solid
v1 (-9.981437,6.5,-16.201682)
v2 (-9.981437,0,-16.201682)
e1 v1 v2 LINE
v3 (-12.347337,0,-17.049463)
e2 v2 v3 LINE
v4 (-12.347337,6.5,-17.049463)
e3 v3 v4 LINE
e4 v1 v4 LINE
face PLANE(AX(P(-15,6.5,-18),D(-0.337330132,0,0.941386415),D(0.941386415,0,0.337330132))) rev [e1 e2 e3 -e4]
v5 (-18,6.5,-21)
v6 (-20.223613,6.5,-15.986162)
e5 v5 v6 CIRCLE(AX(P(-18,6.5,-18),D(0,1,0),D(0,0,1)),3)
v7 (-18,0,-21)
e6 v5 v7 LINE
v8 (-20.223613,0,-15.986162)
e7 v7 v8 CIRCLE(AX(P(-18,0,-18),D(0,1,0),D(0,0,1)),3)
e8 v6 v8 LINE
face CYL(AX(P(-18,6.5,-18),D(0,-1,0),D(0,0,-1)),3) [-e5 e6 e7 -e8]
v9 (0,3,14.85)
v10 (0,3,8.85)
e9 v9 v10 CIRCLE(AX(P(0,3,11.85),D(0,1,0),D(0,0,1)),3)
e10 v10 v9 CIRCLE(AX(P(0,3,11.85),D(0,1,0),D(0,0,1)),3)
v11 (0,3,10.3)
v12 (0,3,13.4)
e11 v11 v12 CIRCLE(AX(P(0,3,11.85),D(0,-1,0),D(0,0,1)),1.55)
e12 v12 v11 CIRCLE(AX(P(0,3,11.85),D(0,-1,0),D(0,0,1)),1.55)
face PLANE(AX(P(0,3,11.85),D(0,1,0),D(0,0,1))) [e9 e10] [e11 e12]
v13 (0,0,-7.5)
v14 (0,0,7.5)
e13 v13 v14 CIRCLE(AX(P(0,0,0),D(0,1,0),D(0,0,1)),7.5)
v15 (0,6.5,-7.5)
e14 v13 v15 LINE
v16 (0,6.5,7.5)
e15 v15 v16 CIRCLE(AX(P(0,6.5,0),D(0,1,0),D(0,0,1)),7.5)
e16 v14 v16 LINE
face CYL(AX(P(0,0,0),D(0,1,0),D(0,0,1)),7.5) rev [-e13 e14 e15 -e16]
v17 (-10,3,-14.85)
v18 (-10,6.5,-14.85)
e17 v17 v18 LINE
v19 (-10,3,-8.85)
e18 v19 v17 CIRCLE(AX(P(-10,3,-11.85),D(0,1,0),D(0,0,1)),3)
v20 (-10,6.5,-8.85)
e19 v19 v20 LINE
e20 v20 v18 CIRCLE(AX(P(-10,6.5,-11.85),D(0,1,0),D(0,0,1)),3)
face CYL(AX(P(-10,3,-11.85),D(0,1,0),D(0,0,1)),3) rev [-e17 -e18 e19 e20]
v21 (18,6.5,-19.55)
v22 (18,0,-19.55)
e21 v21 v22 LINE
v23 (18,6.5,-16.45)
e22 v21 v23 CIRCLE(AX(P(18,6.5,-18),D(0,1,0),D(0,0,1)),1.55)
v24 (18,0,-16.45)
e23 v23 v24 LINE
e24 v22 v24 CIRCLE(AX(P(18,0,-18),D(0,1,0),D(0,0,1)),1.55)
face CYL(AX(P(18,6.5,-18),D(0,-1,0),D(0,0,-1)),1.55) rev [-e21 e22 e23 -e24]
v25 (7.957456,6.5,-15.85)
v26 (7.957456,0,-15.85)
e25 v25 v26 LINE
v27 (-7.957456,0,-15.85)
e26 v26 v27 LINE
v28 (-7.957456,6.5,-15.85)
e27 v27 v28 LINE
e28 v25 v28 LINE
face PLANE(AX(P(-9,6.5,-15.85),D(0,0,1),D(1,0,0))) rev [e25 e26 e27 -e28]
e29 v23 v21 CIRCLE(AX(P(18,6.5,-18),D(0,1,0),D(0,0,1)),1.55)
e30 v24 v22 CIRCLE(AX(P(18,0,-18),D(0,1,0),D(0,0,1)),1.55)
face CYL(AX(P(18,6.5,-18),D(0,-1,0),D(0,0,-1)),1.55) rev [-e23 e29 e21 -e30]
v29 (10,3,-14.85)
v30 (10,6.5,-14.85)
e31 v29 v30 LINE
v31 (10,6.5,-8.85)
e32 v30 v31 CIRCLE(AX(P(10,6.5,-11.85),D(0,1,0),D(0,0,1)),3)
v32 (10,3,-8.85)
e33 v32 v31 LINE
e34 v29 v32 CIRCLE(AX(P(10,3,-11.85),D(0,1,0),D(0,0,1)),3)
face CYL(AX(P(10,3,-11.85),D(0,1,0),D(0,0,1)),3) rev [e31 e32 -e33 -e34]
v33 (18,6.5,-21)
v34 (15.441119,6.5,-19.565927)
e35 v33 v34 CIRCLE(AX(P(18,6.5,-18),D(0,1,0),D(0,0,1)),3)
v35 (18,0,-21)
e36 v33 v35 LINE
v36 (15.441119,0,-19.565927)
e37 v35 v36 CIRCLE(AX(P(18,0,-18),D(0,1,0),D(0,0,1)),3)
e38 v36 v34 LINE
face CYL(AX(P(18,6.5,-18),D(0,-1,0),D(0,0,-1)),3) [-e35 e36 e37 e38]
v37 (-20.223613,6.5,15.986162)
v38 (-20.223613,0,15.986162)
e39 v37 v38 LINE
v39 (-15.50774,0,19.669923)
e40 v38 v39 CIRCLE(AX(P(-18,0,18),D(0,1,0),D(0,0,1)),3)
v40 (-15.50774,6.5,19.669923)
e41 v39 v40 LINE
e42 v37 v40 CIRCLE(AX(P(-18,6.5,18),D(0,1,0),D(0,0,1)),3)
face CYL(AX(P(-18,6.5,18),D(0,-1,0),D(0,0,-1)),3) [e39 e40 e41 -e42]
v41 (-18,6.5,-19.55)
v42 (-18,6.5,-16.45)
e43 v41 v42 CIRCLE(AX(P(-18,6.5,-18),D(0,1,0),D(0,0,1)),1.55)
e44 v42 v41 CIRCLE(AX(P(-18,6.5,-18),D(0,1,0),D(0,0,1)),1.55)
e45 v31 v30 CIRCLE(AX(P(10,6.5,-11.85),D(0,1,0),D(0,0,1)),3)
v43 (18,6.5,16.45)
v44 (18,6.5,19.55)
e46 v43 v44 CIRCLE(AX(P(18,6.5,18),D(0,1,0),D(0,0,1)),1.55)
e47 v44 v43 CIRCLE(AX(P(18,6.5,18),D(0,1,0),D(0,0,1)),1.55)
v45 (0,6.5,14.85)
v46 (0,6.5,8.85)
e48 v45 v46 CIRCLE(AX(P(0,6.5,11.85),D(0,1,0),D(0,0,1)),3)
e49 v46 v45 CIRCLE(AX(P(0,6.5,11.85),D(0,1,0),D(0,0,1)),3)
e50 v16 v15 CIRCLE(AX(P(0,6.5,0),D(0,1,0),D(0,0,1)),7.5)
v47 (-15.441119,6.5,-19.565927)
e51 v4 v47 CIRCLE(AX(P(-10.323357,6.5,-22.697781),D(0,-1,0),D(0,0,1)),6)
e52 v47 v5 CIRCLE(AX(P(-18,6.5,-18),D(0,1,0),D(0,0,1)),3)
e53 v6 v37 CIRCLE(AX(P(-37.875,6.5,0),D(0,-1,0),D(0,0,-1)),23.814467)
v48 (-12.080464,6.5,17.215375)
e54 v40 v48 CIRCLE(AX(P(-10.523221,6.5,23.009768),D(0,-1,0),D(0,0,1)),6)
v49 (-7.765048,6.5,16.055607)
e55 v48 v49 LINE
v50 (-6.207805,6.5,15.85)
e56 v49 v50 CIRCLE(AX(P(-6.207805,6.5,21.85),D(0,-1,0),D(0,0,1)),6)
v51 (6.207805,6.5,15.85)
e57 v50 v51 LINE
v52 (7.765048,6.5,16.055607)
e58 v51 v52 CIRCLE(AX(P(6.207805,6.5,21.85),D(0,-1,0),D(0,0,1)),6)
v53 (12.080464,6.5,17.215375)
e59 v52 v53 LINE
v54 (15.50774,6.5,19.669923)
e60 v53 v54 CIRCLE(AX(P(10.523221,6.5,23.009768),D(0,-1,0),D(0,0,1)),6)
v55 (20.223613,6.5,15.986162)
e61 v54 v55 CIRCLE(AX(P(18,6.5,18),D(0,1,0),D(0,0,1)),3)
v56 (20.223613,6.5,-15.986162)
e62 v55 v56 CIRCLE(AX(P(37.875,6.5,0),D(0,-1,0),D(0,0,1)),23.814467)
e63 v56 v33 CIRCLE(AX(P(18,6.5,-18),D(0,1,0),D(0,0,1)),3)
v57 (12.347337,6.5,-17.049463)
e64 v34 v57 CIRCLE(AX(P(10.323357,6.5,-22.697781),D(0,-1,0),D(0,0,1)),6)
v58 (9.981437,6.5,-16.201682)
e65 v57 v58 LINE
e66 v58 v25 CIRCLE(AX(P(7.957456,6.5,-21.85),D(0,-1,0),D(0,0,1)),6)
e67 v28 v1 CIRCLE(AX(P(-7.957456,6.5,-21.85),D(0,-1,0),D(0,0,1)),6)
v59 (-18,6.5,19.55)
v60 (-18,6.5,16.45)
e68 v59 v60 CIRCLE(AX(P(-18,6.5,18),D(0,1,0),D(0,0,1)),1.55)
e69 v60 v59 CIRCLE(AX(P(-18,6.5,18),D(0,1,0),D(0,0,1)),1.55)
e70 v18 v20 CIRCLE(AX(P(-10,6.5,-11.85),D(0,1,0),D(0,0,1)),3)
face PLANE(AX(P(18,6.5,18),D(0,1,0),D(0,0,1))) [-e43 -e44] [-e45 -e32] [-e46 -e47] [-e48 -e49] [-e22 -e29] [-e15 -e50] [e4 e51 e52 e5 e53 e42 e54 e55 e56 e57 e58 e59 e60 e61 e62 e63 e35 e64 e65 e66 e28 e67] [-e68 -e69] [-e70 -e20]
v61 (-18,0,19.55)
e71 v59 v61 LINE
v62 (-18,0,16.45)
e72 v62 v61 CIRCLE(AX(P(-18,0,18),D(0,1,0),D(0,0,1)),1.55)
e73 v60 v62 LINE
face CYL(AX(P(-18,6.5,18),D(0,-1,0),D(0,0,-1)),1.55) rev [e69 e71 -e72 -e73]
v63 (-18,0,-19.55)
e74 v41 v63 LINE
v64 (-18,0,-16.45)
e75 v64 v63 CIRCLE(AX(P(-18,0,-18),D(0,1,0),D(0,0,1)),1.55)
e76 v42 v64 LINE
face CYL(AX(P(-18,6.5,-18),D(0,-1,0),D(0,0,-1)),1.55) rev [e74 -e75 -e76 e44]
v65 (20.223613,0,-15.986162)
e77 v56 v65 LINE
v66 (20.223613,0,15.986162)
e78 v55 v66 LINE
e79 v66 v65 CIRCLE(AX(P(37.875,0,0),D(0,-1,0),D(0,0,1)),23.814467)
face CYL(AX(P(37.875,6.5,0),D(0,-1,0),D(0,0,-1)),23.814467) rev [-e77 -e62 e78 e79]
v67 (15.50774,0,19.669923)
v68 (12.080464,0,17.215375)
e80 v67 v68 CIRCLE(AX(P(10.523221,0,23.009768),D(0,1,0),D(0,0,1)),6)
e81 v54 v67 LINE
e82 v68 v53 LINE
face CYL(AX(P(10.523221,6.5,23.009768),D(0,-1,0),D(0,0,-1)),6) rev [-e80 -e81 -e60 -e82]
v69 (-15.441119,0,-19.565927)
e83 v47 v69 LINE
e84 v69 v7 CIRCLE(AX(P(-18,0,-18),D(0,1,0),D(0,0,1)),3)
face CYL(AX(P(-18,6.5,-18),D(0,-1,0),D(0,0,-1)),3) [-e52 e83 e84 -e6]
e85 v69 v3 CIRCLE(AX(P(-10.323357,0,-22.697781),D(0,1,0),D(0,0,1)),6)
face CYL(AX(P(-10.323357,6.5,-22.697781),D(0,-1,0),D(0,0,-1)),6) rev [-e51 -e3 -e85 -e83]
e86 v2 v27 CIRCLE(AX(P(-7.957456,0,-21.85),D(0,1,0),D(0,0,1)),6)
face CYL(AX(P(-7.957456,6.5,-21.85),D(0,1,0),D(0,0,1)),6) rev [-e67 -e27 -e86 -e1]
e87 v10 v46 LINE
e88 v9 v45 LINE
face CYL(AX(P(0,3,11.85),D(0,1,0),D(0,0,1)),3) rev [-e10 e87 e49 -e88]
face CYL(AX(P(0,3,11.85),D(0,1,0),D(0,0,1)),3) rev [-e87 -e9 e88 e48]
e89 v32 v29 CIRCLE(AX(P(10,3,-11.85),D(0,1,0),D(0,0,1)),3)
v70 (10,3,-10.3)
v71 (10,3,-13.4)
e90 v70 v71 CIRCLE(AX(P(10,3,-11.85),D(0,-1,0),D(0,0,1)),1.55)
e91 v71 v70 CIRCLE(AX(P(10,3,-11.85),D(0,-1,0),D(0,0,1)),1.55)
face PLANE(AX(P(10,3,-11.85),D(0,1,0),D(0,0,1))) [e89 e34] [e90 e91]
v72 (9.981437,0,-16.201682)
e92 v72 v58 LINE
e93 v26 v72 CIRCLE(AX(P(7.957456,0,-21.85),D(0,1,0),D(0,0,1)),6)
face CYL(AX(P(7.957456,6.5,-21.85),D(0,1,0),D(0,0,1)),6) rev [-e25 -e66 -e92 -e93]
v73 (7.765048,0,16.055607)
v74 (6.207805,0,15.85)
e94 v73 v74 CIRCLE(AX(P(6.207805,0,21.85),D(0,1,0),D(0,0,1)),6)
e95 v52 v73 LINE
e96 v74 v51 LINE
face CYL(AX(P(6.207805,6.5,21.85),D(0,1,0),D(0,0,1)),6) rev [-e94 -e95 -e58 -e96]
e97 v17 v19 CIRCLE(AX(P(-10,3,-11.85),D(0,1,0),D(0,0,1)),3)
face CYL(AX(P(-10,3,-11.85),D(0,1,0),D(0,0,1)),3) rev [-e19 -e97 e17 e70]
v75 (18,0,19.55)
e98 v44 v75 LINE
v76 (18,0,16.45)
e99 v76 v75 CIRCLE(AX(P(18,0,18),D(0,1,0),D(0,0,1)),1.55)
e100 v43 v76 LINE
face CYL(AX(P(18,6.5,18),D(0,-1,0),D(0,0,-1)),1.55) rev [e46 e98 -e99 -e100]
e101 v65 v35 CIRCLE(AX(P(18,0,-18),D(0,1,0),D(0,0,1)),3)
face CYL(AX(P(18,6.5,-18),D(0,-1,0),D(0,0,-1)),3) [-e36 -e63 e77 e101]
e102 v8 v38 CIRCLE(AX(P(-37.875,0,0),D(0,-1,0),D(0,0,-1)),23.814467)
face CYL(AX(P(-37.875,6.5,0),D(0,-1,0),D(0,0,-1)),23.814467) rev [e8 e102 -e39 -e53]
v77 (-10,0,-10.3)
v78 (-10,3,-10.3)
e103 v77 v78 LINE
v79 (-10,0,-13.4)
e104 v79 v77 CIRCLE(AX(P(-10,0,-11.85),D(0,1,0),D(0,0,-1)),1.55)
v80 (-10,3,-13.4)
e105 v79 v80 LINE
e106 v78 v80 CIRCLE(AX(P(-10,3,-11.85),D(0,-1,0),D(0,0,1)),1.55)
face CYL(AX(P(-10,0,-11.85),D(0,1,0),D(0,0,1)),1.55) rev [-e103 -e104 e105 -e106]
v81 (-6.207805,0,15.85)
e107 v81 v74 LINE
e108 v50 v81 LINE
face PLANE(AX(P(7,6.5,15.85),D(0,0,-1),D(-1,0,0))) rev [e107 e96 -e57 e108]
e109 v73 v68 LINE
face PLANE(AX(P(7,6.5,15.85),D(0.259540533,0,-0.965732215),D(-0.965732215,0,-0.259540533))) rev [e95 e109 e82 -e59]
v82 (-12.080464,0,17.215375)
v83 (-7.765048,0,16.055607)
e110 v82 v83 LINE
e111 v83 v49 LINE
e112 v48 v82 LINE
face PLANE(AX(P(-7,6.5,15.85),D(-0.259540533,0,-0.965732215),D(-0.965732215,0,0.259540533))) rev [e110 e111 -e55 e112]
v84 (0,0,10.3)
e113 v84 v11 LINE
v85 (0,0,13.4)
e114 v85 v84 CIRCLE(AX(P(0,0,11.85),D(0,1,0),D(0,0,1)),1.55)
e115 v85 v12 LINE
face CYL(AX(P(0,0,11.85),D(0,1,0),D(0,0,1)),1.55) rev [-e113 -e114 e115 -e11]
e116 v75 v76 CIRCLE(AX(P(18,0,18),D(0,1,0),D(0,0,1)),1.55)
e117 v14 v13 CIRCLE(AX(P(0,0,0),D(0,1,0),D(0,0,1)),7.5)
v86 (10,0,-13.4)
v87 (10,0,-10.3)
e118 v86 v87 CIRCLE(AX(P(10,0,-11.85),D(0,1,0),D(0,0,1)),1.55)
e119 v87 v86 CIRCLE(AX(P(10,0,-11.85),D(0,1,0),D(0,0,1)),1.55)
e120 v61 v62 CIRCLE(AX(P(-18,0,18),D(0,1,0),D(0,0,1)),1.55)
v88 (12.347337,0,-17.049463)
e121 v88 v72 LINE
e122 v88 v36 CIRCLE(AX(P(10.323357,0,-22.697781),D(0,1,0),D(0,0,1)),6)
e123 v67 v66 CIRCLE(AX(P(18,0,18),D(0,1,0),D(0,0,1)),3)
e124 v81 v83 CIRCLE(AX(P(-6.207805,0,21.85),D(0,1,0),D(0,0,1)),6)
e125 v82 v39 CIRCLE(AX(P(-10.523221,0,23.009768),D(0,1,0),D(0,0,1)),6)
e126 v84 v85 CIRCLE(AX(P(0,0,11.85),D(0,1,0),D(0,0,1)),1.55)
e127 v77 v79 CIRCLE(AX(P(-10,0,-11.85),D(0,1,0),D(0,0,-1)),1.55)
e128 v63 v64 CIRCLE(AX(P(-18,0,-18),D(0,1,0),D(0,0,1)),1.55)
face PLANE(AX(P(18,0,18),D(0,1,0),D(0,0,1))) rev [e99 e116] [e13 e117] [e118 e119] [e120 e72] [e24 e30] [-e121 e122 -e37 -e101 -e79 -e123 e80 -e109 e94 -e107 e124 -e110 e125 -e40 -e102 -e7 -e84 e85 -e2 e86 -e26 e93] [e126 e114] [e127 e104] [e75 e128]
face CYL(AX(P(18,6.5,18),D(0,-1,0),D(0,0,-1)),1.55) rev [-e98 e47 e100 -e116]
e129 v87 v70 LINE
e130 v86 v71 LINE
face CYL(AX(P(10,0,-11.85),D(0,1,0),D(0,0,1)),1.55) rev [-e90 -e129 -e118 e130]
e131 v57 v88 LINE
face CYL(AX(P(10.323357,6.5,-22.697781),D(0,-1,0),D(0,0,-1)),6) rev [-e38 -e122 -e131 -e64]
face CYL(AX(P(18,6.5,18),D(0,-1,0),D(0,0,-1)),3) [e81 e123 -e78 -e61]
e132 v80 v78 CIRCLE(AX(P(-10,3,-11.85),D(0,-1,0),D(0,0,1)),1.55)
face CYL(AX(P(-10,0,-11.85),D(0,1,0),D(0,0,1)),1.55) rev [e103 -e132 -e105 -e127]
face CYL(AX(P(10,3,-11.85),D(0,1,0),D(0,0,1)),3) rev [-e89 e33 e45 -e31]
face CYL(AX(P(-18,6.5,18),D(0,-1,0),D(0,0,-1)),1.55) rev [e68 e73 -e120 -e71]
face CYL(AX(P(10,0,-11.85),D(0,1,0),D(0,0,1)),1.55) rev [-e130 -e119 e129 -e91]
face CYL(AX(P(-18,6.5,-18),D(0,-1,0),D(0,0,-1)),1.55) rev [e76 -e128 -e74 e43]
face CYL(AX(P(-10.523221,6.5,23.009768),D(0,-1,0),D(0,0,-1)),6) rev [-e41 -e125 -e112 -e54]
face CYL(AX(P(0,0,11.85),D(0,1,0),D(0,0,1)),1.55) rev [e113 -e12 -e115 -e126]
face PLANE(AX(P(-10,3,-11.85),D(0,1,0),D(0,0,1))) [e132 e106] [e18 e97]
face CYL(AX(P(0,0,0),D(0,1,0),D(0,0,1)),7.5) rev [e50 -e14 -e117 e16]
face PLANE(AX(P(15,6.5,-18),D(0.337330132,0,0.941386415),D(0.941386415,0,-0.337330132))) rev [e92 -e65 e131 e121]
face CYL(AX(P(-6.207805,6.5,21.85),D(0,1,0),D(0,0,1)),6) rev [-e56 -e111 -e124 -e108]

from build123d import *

# Parameters (mm, degrees)
SKETCH_1_R           = 1.55
EXTRUDE_1_DEPTH      = 6.5
FILLET_1_R           = 6
SKETCH_9_R           = 7.5
SKETCH_9_R_2         = 1.55
CUT_EXTRUDE_11_DEPTH = 31.401480227
SKETCH_10_R          = 3
CUT_EXTRUDE_12_DEPTH = 3.5


with BuildPart() as part:
    # 草图1 → 凸台-拉伸1 (new body)
    with BuildSketch(Plane(origin=(0, 0, 0), x_dir=(1, 0, 0), z_dir=(0, 1, 0))):
        with BuildLine():
            Line((-15, 18), (-9, 15.85))
            Line((-9, 15.85), (9, 15.85))
            Line((9, 15.85), (15, 18))
            ThreePointArc((15, 18), (19.079157226, 20.799181966), (20.223613121, 15.986161702))
            ThreePointArc((20.223613121, 15.986161702), (14.060533289, 0), (20.223613121, -15.986161702))
            ThreePointArc((20.223613121, -15.986161702), (19.079157226, -20.799181966), (15, -18))
            Line((15, -18), (7, -15.85))
            Line((7, -15.85), (-7, -15.85))
            Line((-7, -15.85), (-15, -18))
            ThreePointArc((-15, -18), (-19.079157226, -20.799181966), (-20.223613121, -15.986161702))
            ThreePointArc((-20.223613121, -15.986161702), (-14.060533289, 0), (-20.223613121, 15.986161702))
            ThreePointArc((-20.223613121, 15.986161702), (-19.079157226, 20.799181966), (-15, 18))
        make_face()
        with Locations(Location((18, 18, 0), (0, 0, 90))):
            Circle(SKETCH_1_R, mode=Mode.SUBTRACT)
        with Locations(Location((18, -18, 0), (0, 0, 90))):
            Circle(SKETCH_1_R, mode=Mode.SUBTRACT)
        with Locations(Location((-18, -18, 0), (0, 0, 90))):
            Circle(SKETCH_1_R, mode=Mode.SUBTRACT)
        with Locations(Location((-18, 18, 0), (0, 0, 90))):
            Circle(SKETCH_1_R, mode=Mode.SUBTRACT)
    extrude(amount=EXTRUDE_1_DEPTH)

    # 圆角1
    fillet_1_edges = [part.edges().sort_by_distance(p)[0] for p in [
        (15, 3.25, 18),
        (7, 3.25, 15.85),
        (-7, 3.25, 15.85),
        (-15, 3.25, 18),
        (-15, 3.25, -18),
        (-9, 3.25, -15.85),
        (9, 3.25, -15.85),
        (15, 3.25, -18),
    ]]
    fillet(fillet_1_edges, radius=FILLET_1_R)

    # 草图9 → 切除-拉伸11 (cut, through all)
    with BuildSketch(Plane(origin=(0, 6.5, 0), x_dir=(1, 0, 0), z_dir=(0, 1, 0))):
        with Locations(Location((0, 0, 0), (0, 0, 270))):
            Circle(SKETCH_9_R)
        with Locations(Location((10, 11.85, 0), (0, 0, 270))):
            Circle(SKETCH_9_R_2)
        with Locations(Location((0, -11.85, 0), (0, 0, 270))):
            Circle(SKETCH_9_R_2)
        with Locations(Location((-10, 11.85, 0), (0, 0, 270))):
            Circle(SKETCH_9_R_2)
    extrude(amount=-CUT_EXTRUDE_11_DEPTH, mode=Mode.SUBTRACT)

    # 草图10 → 切除-拉伸12 (cut)
    with BuildSketch(Plane(origin=(0, 6.5, 0), x_dir=(1, 0, 0), z_dir=(0, 1, 0))):
        with Locations(Location((-10, 11.85, 0), (0, 0, 270))):
            Circle(SKETCH_10_R)
        with Locations(Location((10, 11.85, 0), (0, 0, 270))):
            Circle(SKETCH_10_R)
        with Locations(Location((0, -11.85, 0), (0, 0, 270))):
            Circle(SKETCH_10_R)
    extrude(amount=-CUT_EXTRUDE_12_DEPTH, mode=Mode.SUBTRACT)


solid = part.part
